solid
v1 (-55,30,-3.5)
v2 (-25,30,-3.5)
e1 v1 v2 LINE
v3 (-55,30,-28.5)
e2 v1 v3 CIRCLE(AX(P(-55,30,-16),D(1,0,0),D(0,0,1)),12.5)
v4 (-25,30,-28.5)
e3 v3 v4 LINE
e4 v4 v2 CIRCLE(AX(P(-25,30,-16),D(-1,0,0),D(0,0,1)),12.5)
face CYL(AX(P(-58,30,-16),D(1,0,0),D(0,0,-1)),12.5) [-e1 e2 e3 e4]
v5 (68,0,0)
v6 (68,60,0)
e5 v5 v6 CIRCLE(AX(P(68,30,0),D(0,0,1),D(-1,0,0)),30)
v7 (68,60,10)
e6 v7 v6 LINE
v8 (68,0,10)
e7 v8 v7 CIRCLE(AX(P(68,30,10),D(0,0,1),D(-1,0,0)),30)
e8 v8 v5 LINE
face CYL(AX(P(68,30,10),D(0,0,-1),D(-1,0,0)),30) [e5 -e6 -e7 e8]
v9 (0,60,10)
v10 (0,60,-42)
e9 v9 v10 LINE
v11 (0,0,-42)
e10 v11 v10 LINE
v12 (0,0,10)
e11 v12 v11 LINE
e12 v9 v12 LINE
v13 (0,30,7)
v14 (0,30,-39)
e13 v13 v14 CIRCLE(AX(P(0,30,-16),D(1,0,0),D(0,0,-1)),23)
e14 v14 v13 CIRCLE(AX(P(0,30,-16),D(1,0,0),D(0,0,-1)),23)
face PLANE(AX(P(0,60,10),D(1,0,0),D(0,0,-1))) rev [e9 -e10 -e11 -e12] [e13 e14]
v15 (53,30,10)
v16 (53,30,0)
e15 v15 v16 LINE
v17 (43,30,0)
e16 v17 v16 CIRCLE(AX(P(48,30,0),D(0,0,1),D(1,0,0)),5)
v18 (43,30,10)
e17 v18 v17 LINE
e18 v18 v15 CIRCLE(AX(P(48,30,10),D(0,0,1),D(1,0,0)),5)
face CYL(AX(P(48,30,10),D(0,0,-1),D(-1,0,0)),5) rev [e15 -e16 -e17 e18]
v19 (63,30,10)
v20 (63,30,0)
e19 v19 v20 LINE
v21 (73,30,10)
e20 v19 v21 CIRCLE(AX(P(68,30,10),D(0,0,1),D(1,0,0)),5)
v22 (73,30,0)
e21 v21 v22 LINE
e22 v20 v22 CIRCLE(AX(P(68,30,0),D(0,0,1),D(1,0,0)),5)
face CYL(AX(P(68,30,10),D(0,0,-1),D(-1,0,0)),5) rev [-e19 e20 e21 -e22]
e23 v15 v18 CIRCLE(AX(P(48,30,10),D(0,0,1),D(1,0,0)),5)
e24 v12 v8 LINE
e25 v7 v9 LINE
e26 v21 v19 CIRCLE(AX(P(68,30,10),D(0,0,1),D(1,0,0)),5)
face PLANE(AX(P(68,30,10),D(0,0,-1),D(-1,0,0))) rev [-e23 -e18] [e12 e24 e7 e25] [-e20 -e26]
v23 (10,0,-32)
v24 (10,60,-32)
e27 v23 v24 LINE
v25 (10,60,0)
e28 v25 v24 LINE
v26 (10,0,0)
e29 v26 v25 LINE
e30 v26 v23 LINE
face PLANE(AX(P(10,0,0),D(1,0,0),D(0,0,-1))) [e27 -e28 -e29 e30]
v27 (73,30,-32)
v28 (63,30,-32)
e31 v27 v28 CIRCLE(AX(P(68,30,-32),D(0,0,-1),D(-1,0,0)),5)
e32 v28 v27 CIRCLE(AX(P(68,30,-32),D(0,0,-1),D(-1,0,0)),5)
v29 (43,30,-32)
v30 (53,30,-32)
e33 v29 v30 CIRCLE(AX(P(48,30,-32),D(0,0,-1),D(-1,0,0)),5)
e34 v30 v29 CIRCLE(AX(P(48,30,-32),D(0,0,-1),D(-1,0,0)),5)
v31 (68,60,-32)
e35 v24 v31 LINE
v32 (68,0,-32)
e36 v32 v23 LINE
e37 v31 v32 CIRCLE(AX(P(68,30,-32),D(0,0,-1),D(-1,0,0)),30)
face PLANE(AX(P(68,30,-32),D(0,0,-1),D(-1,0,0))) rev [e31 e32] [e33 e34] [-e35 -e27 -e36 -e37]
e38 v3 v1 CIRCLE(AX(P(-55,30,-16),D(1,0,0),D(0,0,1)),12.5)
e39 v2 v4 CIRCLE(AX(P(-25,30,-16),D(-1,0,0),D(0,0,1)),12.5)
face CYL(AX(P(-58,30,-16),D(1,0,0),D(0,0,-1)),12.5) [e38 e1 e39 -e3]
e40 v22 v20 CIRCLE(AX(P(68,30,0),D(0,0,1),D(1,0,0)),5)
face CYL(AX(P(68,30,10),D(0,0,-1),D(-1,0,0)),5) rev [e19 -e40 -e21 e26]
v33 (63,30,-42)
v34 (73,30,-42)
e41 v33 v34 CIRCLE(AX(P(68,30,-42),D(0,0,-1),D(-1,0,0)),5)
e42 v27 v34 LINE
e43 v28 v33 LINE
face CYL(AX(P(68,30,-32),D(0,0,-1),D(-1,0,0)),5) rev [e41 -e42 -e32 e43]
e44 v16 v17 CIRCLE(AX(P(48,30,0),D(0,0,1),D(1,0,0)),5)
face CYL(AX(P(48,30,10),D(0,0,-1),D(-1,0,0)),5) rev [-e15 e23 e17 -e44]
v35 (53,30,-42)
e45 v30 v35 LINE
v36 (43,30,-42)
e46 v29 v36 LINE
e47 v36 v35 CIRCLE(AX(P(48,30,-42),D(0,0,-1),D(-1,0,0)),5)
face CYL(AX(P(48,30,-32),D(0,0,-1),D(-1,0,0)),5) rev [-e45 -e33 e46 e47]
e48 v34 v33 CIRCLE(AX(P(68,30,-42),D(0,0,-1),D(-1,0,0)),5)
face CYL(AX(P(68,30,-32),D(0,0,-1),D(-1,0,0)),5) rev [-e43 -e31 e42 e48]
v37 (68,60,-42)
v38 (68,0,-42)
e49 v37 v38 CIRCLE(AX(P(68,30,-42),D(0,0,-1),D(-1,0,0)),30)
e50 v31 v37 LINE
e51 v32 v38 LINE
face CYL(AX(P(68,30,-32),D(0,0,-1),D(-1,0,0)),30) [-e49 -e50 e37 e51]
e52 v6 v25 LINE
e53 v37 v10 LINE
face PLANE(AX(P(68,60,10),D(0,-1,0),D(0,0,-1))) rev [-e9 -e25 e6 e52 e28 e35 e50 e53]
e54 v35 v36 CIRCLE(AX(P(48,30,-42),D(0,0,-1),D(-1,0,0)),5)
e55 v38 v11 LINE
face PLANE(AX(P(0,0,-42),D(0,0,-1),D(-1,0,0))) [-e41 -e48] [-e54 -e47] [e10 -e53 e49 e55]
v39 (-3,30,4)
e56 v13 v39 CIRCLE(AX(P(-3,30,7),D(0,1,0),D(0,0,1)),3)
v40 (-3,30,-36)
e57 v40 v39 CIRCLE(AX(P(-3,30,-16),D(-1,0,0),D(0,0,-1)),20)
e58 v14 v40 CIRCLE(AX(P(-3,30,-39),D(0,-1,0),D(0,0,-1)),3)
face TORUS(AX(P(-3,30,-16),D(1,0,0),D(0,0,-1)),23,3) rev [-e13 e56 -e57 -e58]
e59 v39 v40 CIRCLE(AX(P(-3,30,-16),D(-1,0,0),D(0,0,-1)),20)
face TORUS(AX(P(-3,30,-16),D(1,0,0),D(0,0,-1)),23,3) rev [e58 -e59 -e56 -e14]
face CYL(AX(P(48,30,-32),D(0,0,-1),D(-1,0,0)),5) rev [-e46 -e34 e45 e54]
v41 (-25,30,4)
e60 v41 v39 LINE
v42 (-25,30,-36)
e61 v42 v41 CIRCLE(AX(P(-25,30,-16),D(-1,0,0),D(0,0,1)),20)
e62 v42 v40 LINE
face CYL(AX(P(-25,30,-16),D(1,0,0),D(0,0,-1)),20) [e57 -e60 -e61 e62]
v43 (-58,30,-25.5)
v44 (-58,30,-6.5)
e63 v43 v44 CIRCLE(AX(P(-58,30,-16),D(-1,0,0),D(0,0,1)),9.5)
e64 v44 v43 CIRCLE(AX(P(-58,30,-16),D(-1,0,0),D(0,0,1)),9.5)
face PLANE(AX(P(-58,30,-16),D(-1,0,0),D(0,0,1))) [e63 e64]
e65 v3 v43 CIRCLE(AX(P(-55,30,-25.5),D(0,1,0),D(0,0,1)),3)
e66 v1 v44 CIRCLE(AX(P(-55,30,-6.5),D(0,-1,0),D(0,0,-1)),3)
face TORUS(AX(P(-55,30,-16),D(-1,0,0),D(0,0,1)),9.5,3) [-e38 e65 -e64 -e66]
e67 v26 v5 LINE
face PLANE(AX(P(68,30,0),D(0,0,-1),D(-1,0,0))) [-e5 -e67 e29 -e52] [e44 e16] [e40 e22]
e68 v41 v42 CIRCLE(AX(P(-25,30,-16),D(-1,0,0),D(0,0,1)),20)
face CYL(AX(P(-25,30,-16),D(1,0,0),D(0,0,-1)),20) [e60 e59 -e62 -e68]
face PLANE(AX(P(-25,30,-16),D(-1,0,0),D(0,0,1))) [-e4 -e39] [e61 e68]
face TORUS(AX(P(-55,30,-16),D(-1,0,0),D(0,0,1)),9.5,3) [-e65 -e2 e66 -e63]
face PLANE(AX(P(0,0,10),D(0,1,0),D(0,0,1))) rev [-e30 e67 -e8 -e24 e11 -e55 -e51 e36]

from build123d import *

# Parameters (mm, degrees)
FRONT_EAR_PROFILE_SKETCH_R = 5
FRONT_EAR_PLATE_DEPTH      = 10
BRIDGE_WALL_SKETCH_W       = 10
BRIDGE_WALL_SKETCH_H       = 42
BRIDGE_WALL_DEPTH          = 60
REAR_EAR_PROFILE_SKETCH_R  = 5
REAR_EAR_PLATE_DEPTH       = 10
COLLAR_SKETCH_26_R         = 20
SHANK_COLLAR_26_DEPTH      = 25
COLLAR_FILLET_R3_R         = 3
PIN_SHANK_SKETCH_R         = 12.5
PIN_SHANK_DEPTH            = 33
SHANK_END_FILLET_R3_R      = 3


with BuildPart() as part:
    # Front Ear Profile Sketch → Front Ear Plate (new body)
    with BuildSketch(Plane.XY):
        with BuildLine():
            Line((0, 0), (68, 0))
            ThreePointArc((68, 0), (98, 30), (68, 60))
            Line((68, 60), (0, 60))
            Line((0, 60), (0, 0))
        make_face()
        with Locations((68, 30)):
            Circle(FRONT_EAR_PROFILE_SKETCH_R, mode=Mode.SUBTRACT)
        with Locations((48, 30)):
            Circle(FRONT_EAR_PROFILE_SKETCH_R, mode=Mode.SUBTRACT)
    extrude(amount=FRONT_EAR_PLATE_DEPTH)

    # Bridge Wall Sketch → Bridge Wall (add)
    with BuildSketch(Plane(origin=(0, 60, 0), x_dir=(1, 0, 0), z_dir=(0, 1, 0))):
        with Locations((5, 21)):
            Rectangle(BRIDGE_WALL_SKETCH_W, BRIDGE_WALL_SKETCH_H)
    extrude(amount=-BRIDGE_WALL_DEPTH)

    # Rear Ear Profile Sketch → Rear Ear Plate (add)
    with BuildSketch(Plane(origin=(0, 0, -42), x_dir=(-1, 0, 0), z_dir=(0, 0, -1))):
        with BuildLine():
            Line((-10, 60), (-68, 60))
            ThreePointArc((-68, 60), (-98, 30), (-68, 0))
            Line((-68, 0), (-10, 0))
            Line((-10, 0), (-10, 60))
        make_face()
        with Locations(Location((-68, 30, 0), (0, 0, 180))):
            Circle(REAR_EAR_PROFILE_SKETCH_R, mode=Mode.SUBTRACT)
        with Locations(Location((-48, 30, 0), (0, 0, 180))):
            Circle(REAR_EAR_PROFILE_SKETCH_R, mode=Mode.SUBTRACT)
    extrude(amount=-REAR_EAR_PLATE_DEPTH)

    # Collar Sketch Ø26 → Shank Collar Ø26 (add)
    with BuildSketch(Plane.ZY):
        with Locations((-16, 30)):
            Circle(COLLAR_SKETCH_26_R)
    extrude(amount=SHANK_COLLAR_26_DEPTH)

    # Collar Fillet R3
    collar_fillet_r3_edges = [part.edges().sort_by_distance(p)[0] for p in [
        (0, 30, -36),
    ]]
    fillet(collar_fillet_r3_edges, radius=COLLAR_FILLET_R3_R)

    # Pin Shank Sketch → Pin Shank (add)
    with BuildSketch(Plane.ZY.offset(25)):
        with Locations((-16, 30)):
            Circle(PIN_SHANK_SKETCH_R)
    extrude(amount=PIN_SHANK_DEPTH)

    # Shank End Fillet R3
    shank_end_fillet_r3_edges = [part.edges().sort_by_distance(p)[0] for p in [
        (-58, 30, -28.5),
    ]]
    fillet(shank_end_fillet_r3_edges, radius=SHANK_END_FILLET_R3_R)


solid = part.part
